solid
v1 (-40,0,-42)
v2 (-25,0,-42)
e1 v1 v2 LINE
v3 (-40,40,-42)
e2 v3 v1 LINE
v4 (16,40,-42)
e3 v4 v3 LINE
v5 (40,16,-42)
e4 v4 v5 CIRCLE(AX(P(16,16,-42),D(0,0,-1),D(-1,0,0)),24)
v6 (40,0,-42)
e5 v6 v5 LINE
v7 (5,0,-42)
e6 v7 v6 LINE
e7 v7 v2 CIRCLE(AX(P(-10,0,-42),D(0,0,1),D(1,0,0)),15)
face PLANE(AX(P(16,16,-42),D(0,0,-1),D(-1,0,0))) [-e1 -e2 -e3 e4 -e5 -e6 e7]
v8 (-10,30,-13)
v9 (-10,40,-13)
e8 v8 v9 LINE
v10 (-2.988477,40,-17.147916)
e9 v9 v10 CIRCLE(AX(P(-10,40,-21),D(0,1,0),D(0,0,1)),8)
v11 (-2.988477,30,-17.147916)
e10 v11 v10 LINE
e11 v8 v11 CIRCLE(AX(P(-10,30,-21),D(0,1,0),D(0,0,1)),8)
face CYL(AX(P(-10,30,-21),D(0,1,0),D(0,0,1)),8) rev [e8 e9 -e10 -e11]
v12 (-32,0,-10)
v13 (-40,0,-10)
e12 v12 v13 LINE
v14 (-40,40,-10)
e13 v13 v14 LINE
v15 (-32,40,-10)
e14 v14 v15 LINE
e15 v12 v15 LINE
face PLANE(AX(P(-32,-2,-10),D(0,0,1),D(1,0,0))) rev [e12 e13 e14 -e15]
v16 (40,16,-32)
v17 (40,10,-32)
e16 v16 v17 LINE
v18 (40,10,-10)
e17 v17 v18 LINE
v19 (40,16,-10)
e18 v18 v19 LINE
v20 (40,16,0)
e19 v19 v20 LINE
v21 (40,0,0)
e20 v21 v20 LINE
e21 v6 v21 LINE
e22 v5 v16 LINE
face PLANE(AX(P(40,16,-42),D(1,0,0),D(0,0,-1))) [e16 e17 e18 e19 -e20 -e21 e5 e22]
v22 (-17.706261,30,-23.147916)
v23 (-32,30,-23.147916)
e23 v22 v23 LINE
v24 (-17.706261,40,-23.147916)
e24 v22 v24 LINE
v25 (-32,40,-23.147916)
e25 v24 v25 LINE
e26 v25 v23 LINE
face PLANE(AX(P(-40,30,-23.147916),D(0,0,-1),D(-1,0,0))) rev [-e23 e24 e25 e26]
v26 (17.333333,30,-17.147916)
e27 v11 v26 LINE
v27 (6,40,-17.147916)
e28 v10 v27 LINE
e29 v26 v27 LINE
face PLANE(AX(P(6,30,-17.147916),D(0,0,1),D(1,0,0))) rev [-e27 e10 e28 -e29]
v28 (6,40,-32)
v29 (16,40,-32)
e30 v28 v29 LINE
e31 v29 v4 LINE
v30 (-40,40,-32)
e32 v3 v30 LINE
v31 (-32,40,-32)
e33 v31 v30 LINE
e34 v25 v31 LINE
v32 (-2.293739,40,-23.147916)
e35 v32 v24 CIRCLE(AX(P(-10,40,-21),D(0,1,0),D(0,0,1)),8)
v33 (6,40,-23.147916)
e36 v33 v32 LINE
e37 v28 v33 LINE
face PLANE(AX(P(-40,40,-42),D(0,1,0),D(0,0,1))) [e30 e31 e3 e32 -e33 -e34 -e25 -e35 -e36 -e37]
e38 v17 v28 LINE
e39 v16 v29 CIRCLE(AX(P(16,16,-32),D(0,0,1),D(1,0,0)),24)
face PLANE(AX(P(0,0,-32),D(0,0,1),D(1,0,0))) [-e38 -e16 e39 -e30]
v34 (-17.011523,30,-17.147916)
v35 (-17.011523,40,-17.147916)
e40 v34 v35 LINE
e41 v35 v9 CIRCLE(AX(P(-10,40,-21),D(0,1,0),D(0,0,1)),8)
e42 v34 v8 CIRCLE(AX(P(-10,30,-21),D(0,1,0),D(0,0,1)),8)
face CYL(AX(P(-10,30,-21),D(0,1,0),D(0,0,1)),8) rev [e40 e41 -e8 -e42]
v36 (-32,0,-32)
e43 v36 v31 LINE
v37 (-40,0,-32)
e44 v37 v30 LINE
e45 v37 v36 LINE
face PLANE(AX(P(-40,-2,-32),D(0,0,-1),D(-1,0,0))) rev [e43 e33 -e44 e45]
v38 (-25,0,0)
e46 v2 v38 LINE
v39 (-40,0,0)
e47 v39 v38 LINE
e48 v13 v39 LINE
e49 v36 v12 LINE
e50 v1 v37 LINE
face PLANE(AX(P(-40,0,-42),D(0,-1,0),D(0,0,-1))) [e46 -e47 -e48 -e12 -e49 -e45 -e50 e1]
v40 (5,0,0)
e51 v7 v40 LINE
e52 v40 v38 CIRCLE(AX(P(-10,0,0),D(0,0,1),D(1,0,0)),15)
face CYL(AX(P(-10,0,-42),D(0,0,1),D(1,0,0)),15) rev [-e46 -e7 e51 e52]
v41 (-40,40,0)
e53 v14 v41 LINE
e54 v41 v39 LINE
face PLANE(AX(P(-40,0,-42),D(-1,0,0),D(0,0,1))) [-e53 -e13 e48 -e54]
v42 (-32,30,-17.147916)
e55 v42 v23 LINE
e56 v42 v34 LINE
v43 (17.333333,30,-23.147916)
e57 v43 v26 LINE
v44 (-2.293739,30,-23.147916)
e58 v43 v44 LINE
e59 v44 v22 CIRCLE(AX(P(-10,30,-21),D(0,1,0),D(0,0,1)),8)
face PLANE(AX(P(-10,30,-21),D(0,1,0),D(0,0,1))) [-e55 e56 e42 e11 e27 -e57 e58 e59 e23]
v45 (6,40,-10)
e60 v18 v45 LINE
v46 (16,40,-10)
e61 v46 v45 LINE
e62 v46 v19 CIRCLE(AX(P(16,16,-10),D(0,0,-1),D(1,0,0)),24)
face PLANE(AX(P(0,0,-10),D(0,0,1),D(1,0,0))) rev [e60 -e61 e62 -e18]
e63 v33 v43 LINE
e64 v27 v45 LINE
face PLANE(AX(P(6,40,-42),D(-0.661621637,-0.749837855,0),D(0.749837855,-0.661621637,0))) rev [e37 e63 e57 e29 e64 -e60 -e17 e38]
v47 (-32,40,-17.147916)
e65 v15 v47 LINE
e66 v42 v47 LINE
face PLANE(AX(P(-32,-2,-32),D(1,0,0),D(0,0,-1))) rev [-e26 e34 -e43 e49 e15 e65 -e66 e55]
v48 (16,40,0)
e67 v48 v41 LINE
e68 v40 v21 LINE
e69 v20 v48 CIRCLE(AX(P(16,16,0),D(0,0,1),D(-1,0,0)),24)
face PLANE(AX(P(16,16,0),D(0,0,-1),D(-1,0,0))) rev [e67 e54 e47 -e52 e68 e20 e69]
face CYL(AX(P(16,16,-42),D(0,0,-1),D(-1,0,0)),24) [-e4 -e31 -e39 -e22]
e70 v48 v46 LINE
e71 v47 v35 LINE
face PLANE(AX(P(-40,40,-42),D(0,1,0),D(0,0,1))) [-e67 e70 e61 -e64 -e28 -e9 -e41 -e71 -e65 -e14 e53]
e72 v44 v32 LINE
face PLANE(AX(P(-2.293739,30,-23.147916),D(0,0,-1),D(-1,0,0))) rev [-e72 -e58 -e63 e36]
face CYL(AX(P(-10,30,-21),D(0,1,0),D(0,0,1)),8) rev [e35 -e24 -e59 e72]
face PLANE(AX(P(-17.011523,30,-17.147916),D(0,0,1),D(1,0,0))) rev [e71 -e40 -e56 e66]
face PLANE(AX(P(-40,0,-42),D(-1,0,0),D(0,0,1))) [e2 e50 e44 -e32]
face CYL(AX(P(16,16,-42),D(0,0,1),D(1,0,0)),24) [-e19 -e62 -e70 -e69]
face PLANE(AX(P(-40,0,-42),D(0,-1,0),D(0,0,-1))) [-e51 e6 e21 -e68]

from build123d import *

# Parameters (mm, degrees)
BRACKET_BODY_DEPTH      = 42
TOP_SLOT_CUT_DEPTH      = 10
THROUGH_SLOT_10MM_DEPTH = 42
SLOT_RELIEF_SKETCH_W    = 6
SLOT_RELIEF_SKETCH_H    = 10
SLOT_RELIEF_CUT_DEPTH   = 42
SIDE_BOSS_A_SKETCH_W    = 80
SIDE_BOSS_A_SKETCH_H    = 40
SIDE_BOSS_A_DEPTH       = 10
SIDE_BOSS_B_SKETCH_W    = 80
SIDE_BOSS_B_SKETCH_H    = 40
SIDE_BOSS_B_DEPTH       = 10
CORNER_ROUND_R24_R      = 24
ARCH_CUTOUT_DEPTH       = 42
NOTCH_SKETCH_W          = 8
NOTCH_SKETCH_H          = 22
NOTCH_CUT_DEPTH         = 42


with BuildPart() as part:
    # Bracket Profile Sketch → Bracket Body (new body)
    with BuildSketch(Plane.XY):
        with BuildLine():
            Line((-40, 0), (40, 0))
            Line((40, 0), (40, 10))
            Line((40, 10), (40, 16))
            ThreePointArc((40, 16), (32.970562748, 32.970562748), (16, 40))
            Line((16, 40), (6, 40))
            Line((6, 40), (-40, 40))
            Line((-40, 40), (-40, 0))
        make_face()
    extrude(amount=-BRACKET_BODY_DEPTH)

    # Top Slot Sketch → Top Slot Cut (cut)
    with BuildSketch(Plane(origin=(0, 40, 0), x_dir=(1, 0, 0), z_dir=(0, 1, 0))):
        with BuildLine():
            Line((-40, 23.147915888), (-17.706260918, 23.147915888))
            ThreePointArc((-17.706260918, 23.147915888), (-10, 29), (-2.293739082, 23.147915888))
            Line((-2.293739082, 23.147915888), (6, 23.147915888))
            Line((6, 23.147915888), (6, 17.147915888))
            Line((6, 17.147915888), (-2.988477484, 17.147915888))
            ThreePointArc((-2.988477484, 17.147915888), (-10, 13), (-17.011522516, 17.147915888))
            Line((-17.011522516, 17.147915888), (-40, 17.147915888))
            Line((-40, 17.147915888), (-40, 23.147915888))
        make_face()
    extrude(amount=-TOP_SLOT_CUT_DEPTH, mode=Mode.SUBTRACT)

    # Through Slot Sketch → Through Slot 10mm (cut)
    with BuildSketch(Plane.XY):
        with BuildLine():
            Line((6, 40), (40, 10))
            Line((40, 10), (40, 16))
            ThreePointArc((40, 16), (32.970562748, 32.970562748), (16, 40))
            Line((16, 40), (6, 40))
        make_face()
    extrude(amount=-THROUGH_SLOT_10MM_DEPTH, mode=Mode.SUBTRACT)

    # Slot Relief Sketch → Slot Relief Cut (cut)
    with BuildSketch(Plane.ZY.offset(-6)):
        with Locations((-20.147915888, 35)):
            Rectangle(SLOT_RELIEF_SKETCH_W, SLOT_RELIEF_SKETCH_H)
    extrude(amount=-SLOT_RELIEF_CUT_DEPTH, mode=Mode.SUBTRACT)

    # Side Boss A Sketch → Side Boss A (add)
    with BuildSketch(Plane.XY):
        with Locations((0, 20)):
            Rectangle(SIDE_BOSS_A_SKETCH_W, SIDE_BOSS_A_SKETCH_H)
    extrude(amount=-SIDE_BOSS_A_DEPTH)

    # Side Boss B Sketch → Side Boss B (add)
    with BuildSketch(Plane(origin=(0, 0, -42), x_dir=(-1, 0, 0), z_dir=(0, 0, -1))):
        with Locations((0, 20)):
            Rectangle(SIDE_BOSS_B_SKETCH_W, SIDE_BOSS_B_SKETCH_H)
    extrude(amount=-SIDE_BOSS_B_DEPTH)

    # Corner Round R24
    corner_round_r24_edges = [part.edges().sort_by_distance(p)[0] for p in [
        (40, 40, -37),
        (40, 40, -5),
    ]]
    fillet(corner_round_r24_edges, radius=CORNER_ROUND_R24_R)

    # Arch Cutout Sketch → Arch Cutout (cut)
    with BuildSketch(Plane.XY):
        with BuildLine():
            Line((-25, 0), (5, 0))
            ThreePointArc((5, 0), (-10, 15), (-25, 0))
        make_face()
    extrude(amount=-ARCH_CUTOUT_DEPTH, mode=Mode.SUBTRACT)

    # Notch Sketch → Notch Cut (cut)
    with BuildSketch(Plane(origin=(0, 40, 0), x_dir=(1, 0, 0), z_dir=(0, 1, 0))):
        with Locations((-36, 21)):
            Rectangle(NOTCH_SKETCH_W, NOTCH_SKETCH_H)
    extrude(amount=-NOTCH_CUT_DEPTH, mode=Mode.SUBTRACT)


solid = part.part
